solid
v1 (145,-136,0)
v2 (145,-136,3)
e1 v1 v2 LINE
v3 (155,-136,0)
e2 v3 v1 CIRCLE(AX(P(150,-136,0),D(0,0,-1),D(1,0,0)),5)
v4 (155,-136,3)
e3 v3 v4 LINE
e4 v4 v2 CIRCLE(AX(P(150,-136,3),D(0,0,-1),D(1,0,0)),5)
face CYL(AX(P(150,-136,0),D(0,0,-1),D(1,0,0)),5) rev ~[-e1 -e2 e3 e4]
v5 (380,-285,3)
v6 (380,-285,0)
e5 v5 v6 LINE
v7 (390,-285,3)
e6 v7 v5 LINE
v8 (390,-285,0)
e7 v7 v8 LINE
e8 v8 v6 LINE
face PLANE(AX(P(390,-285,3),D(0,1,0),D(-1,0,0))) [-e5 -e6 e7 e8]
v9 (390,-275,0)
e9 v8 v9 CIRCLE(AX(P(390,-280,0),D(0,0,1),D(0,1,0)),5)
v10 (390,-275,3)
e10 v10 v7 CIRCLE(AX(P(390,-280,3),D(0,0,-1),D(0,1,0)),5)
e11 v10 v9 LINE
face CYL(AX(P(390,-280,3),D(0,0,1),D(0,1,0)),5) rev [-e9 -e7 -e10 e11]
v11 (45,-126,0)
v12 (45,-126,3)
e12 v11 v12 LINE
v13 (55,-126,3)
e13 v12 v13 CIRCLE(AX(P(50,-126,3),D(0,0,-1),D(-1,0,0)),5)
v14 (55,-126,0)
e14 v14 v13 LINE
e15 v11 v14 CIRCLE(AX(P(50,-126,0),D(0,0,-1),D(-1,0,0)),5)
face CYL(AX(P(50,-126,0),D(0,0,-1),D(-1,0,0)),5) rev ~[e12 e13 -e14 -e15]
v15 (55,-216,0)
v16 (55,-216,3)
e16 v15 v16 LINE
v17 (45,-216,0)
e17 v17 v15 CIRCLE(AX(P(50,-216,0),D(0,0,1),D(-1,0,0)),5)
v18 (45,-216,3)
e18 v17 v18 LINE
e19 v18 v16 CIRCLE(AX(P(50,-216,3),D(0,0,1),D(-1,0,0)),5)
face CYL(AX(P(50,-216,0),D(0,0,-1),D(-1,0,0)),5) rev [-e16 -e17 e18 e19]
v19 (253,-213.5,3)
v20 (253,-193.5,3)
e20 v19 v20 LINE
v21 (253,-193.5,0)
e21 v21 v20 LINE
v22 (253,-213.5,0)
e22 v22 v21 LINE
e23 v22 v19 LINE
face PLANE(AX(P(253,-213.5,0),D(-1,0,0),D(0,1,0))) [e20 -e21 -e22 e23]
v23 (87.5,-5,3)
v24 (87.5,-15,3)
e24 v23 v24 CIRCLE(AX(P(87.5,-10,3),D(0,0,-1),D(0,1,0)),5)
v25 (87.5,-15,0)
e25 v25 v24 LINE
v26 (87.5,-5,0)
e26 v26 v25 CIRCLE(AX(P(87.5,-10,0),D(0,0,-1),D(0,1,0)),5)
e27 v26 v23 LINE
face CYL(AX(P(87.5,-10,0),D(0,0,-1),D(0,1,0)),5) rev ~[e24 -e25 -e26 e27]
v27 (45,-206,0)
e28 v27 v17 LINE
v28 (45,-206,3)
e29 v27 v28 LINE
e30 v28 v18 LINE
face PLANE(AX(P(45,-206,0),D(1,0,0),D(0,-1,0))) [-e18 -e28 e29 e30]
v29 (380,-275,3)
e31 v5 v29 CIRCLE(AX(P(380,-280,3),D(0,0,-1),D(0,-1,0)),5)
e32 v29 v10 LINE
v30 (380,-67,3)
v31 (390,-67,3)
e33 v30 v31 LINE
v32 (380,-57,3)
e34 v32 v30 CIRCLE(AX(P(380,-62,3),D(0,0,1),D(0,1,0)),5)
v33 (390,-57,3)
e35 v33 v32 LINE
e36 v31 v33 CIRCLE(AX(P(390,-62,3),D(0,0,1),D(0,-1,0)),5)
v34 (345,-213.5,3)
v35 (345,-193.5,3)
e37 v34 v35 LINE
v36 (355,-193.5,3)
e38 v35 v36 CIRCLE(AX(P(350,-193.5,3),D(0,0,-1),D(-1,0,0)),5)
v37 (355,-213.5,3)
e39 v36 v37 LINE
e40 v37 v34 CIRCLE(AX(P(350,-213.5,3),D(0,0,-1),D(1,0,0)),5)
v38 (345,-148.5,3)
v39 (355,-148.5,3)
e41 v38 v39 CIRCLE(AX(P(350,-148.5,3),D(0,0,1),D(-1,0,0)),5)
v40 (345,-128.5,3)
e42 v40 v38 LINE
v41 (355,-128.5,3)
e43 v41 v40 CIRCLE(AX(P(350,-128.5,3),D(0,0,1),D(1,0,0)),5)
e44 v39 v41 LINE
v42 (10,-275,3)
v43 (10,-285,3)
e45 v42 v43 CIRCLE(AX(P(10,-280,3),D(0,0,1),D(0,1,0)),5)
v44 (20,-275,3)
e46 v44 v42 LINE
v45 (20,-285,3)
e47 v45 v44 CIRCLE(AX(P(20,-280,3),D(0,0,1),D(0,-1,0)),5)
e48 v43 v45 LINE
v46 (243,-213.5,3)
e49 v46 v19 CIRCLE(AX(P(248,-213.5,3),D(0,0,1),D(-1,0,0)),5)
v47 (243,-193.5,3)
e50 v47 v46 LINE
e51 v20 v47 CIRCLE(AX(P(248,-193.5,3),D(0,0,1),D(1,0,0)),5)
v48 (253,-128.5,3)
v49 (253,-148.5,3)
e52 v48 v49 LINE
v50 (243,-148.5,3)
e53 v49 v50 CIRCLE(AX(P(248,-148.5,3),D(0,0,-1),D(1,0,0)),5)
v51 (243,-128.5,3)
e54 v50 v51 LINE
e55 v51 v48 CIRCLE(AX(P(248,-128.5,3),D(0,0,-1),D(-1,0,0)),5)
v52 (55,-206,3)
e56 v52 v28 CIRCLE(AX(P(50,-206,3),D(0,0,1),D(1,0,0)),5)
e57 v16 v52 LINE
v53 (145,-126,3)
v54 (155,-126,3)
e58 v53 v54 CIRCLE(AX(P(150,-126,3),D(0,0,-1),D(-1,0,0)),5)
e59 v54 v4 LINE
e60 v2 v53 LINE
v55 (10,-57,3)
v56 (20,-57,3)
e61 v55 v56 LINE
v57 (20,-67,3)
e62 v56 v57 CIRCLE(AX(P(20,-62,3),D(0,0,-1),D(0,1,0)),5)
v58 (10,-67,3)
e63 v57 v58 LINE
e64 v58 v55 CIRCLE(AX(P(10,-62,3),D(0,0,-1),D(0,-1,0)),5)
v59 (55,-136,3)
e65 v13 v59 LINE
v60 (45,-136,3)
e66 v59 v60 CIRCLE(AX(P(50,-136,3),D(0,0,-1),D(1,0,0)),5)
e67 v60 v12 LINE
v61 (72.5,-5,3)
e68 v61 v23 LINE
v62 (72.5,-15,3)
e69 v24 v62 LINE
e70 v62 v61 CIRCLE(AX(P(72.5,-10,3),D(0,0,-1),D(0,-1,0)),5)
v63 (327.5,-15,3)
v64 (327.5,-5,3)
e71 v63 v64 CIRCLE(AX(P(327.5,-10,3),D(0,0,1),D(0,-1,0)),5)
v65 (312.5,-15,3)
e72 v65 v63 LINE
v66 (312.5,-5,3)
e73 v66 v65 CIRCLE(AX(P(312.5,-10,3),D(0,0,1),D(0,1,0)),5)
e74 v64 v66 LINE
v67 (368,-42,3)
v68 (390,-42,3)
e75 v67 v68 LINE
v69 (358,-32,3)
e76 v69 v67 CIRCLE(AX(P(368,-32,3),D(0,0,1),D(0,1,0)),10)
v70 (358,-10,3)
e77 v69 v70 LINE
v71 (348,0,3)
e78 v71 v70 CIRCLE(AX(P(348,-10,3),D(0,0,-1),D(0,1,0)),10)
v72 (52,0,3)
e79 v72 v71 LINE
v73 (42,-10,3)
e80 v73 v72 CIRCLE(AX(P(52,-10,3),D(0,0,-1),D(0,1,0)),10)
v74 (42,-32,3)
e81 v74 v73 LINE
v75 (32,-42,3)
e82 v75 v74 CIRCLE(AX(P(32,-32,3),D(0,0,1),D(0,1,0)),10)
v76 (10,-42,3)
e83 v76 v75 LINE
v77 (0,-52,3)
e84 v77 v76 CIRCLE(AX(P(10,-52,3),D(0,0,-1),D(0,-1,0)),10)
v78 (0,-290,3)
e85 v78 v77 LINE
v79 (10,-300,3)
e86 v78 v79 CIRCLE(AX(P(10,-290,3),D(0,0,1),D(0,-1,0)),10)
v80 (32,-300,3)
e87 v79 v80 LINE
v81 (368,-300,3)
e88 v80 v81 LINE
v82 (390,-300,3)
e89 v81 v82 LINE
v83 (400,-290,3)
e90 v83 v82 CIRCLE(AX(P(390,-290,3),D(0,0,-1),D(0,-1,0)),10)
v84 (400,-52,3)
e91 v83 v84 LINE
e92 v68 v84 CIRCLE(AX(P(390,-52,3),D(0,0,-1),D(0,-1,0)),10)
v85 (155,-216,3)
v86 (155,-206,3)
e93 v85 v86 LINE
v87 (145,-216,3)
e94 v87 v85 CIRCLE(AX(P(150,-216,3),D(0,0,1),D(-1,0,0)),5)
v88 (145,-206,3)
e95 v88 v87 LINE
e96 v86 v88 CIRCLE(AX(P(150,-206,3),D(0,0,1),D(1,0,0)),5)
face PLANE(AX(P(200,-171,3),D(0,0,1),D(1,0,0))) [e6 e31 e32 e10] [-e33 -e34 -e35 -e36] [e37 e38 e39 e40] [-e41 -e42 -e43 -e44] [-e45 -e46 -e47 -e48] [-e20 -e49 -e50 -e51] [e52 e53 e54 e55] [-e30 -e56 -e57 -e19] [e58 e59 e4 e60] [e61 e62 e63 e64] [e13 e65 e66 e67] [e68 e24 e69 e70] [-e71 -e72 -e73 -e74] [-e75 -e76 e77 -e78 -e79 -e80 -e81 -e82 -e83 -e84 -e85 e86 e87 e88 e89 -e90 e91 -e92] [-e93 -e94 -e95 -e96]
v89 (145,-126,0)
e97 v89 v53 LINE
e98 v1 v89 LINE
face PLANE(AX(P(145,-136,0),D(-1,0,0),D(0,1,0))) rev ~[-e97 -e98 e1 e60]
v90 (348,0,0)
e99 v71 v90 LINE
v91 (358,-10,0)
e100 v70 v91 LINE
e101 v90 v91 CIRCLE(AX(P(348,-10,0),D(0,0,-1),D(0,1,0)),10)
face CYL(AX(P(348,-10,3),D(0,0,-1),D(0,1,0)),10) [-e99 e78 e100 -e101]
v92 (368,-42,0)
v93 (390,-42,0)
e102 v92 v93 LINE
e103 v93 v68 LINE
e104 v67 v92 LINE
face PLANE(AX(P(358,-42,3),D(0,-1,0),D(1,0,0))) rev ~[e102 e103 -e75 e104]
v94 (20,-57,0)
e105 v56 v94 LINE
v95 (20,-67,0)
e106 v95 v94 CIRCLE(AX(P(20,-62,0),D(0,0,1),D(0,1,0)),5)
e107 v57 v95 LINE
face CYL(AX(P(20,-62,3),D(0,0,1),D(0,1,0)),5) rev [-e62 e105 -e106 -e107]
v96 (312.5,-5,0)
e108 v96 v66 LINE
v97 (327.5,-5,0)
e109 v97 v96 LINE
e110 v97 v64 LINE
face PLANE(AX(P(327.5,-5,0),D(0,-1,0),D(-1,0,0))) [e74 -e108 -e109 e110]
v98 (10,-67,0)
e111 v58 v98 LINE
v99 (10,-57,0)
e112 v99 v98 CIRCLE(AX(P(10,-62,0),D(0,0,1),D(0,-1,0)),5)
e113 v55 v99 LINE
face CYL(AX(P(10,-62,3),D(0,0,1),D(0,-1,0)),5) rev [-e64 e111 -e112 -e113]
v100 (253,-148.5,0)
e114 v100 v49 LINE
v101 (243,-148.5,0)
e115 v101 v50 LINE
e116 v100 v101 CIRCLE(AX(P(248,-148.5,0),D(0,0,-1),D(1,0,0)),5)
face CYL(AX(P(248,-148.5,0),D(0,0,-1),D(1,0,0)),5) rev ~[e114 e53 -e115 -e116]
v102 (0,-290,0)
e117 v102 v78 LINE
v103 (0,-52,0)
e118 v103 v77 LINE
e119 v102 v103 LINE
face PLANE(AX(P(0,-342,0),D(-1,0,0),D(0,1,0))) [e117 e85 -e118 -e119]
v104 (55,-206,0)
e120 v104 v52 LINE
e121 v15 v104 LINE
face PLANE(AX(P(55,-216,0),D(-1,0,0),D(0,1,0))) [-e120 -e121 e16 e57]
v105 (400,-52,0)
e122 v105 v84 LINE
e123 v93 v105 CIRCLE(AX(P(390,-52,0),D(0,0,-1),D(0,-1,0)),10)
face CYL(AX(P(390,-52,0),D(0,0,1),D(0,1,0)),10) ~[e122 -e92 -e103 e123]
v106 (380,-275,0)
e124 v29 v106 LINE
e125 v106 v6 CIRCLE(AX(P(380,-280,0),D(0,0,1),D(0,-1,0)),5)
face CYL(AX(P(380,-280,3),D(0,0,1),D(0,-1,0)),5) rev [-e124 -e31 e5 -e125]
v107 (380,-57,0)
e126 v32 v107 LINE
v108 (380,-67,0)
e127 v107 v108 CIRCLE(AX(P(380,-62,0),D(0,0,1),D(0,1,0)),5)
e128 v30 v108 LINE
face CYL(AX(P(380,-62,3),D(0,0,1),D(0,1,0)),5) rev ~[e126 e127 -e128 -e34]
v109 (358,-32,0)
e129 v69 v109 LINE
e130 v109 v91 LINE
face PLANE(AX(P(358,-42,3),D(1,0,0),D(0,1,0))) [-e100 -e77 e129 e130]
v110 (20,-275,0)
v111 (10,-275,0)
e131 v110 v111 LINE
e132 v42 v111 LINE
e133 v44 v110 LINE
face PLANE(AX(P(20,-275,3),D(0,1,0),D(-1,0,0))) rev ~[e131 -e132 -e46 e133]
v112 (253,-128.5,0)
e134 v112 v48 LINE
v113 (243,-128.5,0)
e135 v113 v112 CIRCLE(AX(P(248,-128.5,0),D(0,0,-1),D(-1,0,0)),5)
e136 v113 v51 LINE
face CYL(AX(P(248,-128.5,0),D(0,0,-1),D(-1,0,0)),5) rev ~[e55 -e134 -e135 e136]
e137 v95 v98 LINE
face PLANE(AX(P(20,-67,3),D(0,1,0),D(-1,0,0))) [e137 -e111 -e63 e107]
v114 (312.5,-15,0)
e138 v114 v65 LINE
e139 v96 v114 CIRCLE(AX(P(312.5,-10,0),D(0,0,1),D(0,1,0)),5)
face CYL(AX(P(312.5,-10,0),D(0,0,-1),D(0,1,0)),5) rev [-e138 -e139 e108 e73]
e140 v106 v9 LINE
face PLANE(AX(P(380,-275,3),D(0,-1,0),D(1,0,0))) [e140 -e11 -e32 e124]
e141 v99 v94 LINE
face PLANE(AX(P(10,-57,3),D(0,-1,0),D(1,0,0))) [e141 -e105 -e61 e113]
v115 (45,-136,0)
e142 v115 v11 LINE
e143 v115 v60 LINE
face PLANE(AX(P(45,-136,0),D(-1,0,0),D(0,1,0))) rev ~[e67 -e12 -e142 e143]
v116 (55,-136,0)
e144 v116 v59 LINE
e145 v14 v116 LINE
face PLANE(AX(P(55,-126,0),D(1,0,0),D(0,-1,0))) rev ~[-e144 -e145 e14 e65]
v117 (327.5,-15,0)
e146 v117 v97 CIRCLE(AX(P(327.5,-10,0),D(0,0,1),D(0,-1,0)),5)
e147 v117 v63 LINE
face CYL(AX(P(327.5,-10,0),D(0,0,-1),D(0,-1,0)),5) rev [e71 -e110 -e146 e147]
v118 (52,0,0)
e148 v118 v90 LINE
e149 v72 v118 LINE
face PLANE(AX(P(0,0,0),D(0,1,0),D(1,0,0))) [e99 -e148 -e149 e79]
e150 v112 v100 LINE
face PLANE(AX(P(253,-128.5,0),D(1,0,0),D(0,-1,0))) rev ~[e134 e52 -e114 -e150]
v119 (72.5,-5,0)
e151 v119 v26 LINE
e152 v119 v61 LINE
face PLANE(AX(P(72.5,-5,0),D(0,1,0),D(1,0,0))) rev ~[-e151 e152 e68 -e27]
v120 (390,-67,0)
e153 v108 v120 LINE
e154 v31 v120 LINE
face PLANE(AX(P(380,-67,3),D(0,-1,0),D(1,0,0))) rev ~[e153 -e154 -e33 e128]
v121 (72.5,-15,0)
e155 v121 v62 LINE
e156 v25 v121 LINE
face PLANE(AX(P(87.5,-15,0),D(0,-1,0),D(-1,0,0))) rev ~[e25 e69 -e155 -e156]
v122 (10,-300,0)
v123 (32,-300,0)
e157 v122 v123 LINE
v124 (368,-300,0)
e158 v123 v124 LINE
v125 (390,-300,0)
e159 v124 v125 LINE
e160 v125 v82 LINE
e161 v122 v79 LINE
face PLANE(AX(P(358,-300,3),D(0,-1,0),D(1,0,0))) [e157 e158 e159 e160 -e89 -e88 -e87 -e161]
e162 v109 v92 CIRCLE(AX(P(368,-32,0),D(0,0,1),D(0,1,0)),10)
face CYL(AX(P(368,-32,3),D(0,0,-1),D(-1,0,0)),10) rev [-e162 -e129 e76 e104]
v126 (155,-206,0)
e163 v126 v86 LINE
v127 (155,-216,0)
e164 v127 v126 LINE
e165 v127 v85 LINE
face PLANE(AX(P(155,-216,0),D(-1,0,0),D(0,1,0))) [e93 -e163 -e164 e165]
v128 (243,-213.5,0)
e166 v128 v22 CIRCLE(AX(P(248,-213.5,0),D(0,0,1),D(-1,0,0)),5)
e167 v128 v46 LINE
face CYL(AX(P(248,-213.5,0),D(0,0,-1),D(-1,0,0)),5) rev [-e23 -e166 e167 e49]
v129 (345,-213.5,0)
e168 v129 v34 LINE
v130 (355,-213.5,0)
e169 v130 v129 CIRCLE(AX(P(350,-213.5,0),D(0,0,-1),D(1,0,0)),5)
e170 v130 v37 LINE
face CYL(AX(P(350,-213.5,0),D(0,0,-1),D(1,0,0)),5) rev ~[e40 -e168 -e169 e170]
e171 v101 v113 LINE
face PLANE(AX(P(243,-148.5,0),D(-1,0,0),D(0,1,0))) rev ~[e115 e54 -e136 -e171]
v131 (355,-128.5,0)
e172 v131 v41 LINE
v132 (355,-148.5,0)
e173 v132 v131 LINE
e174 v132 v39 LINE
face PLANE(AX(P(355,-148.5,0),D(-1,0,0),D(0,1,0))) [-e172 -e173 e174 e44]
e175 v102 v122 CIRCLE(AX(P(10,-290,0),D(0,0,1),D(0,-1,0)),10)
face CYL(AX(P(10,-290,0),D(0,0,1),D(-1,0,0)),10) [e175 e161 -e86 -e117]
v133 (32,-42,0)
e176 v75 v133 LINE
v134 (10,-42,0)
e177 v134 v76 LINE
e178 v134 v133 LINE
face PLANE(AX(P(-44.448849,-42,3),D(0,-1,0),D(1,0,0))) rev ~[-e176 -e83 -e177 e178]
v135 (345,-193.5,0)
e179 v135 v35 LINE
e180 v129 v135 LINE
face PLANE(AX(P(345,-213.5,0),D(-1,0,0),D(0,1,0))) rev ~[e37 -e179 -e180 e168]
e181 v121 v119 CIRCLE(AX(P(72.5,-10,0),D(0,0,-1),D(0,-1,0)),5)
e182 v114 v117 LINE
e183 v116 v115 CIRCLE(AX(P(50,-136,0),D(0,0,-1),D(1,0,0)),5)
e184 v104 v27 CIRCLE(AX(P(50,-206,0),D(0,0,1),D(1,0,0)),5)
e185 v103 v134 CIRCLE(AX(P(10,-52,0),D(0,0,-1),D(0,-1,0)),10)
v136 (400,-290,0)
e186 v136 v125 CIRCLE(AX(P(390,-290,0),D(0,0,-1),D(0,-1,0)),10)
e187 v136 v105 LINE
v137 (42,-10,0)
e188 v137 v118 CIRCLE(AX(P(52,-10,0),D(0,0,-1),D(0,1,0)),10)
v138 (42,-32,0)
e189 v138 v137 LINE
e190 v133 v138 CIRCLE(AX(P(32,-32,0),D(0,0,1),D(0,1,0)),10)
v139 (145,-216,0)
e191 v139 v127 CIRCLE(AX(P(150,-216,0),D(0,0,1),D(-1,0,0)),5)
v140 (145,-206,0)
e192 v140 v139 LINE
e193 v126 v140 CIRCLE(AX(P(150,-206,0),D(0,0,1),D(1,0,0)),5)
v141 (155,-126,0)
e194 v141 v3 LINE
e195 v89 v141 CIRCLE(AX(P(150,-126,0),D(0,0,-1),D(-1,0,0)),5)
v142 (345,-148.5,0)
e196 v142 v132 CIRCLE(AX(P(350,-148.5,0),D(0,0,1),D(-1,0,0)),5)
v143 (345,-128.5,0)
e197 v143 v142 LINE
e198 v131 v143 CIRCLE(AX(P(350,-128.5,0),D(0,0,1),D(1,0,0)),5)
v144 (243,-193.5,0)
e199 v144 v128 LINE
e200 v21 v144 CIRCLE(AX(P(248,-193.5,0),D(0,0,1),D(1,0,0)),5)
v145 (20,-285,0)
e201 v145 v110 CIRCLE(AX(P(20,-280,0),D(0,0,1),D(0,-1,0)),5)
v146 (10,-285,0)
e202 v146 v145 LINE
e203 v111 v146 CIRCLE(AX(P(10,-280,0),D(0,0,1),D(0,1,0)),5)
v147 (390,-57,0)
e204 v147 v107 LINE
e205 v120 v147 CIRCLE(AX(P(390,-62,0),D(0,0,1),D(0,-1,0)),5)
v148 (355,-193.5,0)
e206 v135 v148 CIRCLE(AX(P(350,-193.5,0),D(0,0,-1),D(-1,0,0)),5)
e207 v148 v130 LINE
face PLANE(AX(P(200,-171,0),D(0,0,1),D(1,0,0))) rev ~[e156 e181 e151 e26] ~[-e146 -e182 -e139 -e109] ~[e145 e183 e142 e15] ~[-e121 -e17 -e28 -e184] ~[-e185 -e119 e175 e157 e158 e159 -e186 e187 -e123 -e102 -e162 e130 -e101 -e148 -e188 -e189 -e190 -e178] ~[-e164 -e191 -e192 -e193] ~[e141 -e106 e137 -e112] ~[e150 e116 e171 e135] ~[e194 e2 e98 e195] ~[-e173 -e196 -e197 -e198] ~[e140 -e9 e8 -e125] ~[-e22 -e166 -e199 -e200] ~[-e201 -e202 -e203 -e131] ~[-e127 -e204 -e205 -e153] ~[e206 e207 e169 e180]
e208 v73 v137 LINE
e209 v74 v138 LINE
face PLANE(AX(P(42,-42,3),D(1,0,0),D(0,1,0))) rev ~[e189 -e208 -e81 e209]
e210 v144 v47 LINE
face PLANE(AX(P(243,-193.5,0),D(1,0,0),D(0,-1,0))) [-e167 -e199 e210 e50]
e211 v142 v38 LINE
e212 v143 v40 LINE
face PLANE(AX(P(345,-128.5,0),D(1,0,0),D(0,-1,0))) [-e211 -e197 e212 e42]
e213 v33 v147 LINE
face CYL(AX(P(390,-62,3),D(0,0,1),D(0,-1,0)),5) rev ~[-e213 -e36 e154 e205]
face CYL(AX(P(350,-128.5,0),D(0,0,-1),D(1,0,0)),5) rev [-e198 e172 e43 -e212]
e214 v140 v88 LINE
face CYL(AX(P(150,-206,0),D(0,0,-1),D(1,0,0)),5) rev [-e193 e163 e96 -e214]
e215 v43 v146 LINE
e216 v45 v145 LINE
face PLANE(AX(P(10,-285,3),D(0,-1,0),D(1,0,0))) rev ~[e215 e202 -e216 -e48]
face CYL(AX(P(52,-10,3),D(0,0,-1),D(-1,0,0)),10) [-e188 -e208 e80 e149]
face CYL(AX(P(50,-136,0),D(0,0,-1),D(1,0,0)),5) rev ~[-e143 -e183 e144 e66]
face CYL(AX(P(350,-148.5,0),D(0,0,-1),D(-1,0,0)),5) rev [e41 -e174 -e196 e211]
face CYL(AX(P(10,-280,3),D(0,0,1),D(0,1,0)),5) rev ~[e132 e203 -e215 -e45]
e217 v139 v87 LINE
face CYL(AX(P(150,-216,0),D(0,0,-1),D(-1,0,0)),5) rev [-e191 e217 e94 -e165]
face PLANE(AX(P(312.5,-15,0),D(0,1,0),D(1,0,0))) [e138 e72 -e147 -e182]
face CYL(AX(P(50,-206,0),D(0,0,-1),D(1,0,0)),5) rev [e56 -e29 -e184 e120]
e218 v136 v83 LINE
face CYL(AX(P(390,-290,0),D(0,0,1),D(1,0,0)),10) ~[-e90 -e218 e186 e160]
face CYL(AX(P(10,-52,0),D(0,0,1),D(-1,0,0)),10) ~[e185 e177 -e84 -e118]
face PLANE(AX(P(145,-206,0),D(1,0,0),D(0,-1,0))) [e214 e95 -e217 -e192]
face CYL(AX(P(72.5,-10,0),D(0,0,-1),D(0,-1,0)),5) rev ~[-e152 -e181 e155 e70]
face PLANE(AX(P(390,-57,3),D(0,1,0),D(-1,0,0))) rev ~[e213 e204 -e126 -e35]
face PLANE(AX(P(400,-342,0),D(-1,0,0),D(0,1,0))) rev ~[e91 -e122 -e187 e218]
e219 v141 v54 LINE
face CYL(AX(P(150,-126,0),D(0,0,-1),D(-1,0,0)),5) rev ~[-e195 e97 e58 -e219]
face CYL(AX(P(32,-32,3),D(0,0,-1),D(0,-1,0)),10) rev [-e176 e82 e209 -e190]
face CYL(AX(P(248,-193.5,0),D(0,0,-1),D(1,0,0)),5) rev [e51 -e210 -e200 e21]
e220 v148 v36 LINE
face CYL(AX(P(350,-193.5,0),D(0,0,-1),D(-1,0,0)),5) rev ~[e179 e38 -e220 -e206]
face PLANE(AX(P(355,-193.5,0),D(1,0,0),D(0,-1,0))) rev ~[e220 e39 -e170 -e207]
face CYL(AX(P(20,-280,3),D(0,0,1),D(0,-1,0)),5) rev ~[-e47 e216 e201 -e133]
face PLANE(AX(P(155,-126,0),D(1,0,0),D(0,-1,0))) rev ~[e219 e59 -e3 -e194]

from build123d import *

# Parameters (mm, degrees)
SKETCH1_W           = 400
SKETCH1_H           = 342
BOSS_EXTRUDE1_DEPTH = 3
SKETCH3_W           = 86.448848967
SKETCH3_H           = 526.142419803
CUT_EXTRUDE2_DEPTH  = 527.282243668
FILLET1_R           = 10
CUT_EXTRUDE3_DEPTH  = 527.282243668
SKETCH5_W           = 336
SKETCH5_H           = 215.570811559
CUT_EXTRUDE4_DEPTH  = 10


with BuildPart() as part:
    # Sketch1 → Boss-Extrude1 (new body)
    with BuildSketch(Plane.XY):
        with Locations((200, -171)):
            Rectangle(SKETCH1_W, SKETCH1_H)
        with BuildLine():
            Line((253, -128.5), (253, -148.5))
            ThreePointArc((253, -148.5), (248, -153.5), (243, -148.5))
            Line((243, -148.5), (243, -128.5))
            ThreePointArc((243, -128.5), (248, -123.5), (253, -128.5))
        make_face(mode=Mode.SUBTRACT)
        with BuildLine():
            Line((345, -128.5), (345, -148.5))
            ThreePointArc((345, -148.5), (350, -153.5), (355, -148.5))
            Line((355, -148.5), (355, -128.5))
            ThreePointArc((355, -128.5), (350, -123.5), (345, -128.5))
        make_face(mode=Mode.SUBTRACT)
        with BuildLine():
            Line((345, -213.5), (345, -193.5))
            ThreePointArc((345, -193.5), (350, -188.5), (355, -193.5))
            Line((355, -193.5), (355, -213.5))
            ThreePointArc((355, -213.5), (350, -218.5), (345, -213.5))
        make_face(mode=Mode.SUBTRACT)
        with BuildLine():
            Line((253, -213.5), (253, -193.5))
            ThreePointArc((253, -193.5), (248, -188.5), (243, -193.5))
            Line((243, -193.5), (243, -213.5))
            ThreePointArc((243, -213.5), (248, -218.5), (253, -213.5))
        make_face(mode=Mode.SUBTRACT)
        with BuildLine():
            Line((72.5, -5), (87.5, -5))
            ThreePointArc((87.5, -5), (92.5, -10), (87.5, -15))
            Line((87.5, -15), (72.5, -15))
            ThreePointArc((72.5, -15), (67.5, -10), (72.5, -5))
        make_face(mode=Mode.SUBTRACT)
        with BuildLine():
            Line((327.5, -5), (312.5, -5))
            ThreePointArc((312.5, -5), (307.5, -10), (312.5, -15))
            Line((312.5, -15), (327.5, -15))
            ThreePointArc((327.5, -15), (332.5, -10), (327.5, -5))
        make_face(mode=Mode.SUBTRACT)
        with BuildLine():
            Line((327.5, -337), (312.5, -337))
            ThreePointArc((312.5, -337), (307.5, -332), (312.5, -327))
            Line((312.5, -327), (327.5, -327))
            ThreePointArc((327.5, -327), (332.5, -332), (327.5, -337))
        make_face(mode=Mode.SUBTRACT)
        with BuildLine():
            Line((72.5, -337), (87.5, -337))
            ThreePointArc((87.5, -337), (92.5, -332), (87.5, -327))
            Line((87.5, -327), (72.5, -327))
            ThreePointArc((72.5, -327), (67.5, -332), (72.5, -337))
        make_face(mode=Mode.SUBTRACT)
        with BuildLine():
            Line((55, -126), (55, -136))
            ThreePointArc((55, -136), (50, -141), (45, -136))
            Line((45, -136), (45, -126))
            ThreePointArc((45, -126), (50, -121), (55, -126))
        make_face(mode=Mode.SUBTRACT)
        with BuildLine():
            Line((155, -126), (155, -136))
            ThreePointArc((155, -136), (150, -141), (145, -136))
            Line((145, -136), (145, -126))
            ThreePointArc((145, -126), (150, -121), (155, -126))
        make_face(mode=Mode.SUBTRACT)
        with BuildLine():
            Line((155, -216), (155, -206))
            ThreePointArc((155, -206), (150, -201), (145, -206))
            Line((145, -206), (145, -216))
            ThreePointArc((145, -216), (150, -221), (155, -216))
        make_face(mode=Mode.SUBTRACT)
        with BuildLine():
            Line((55, -216), (55, -206))
            ThreePointArc((55, -206), (50, -201), (45, -206))
            Line((45, -206), (45, -216))
            ThreePointArc((45, -216), (50, -221), (55, -216))
        make_face(mode=Mode.SUBTRACT)
    extrude(amount=BOSS_EXTRUDE1_DEPTH)

    # Sketch3 → Cut-Extrude2 (cut, through all)
    with BuildSketch(Plane.XY.offset(3)):
        with Locations((-1.224424484, -563.071209901)):
            Rectangle(SKETCH3_W, SKETCH3_H)
        with Locations((401.224424484, -563.071209901)):
            Rectangle(SKETCH3_W, SKETCH3_H)
        with Locations((401.224424484, 221.071209902)):
            Rectangle(SKETCH3_W, SKETCH3_H)
        with Locations((-1.224424484, 221.071209902)):
            Rectangle(SKETCH3_W, SKETCH3_H)
    extrude(amount=-CUT_EXTRUDE2_DEPTH, mode=Mode.SUBTRACT)

    # Fillet1
    fillet1_edges = [part.edges().sort_by_distance(p)[0] for p in [
        (358, 0, 1.5),
        (42, 0, 1.5),
        (400, -300, 1.5),
        (400, -42, 1.5),
        (42, -342, 1.5),
        (358, -342, 1.5),
        (0, -300, 1.5),
        (0, -42, 1.5),
        (42, -42, 1.5),
        (358, -42, 1.5),
        (358, -300, 1.5),
        (42, -300, 1.5),
    ]]
    fillet(fillet1_edges, radius=FILLET1_R)

    # Sketch4 → Cut-Extrude3 (cut, through all)
    with BuildSketch(Plane.XY.offset(3)):
        with BuildLine():
            Line((10, -57), (20, -57))
            ThreePointArc((20, -57), (25, -62), (20, -67))
            Line((20, -67), (10, -67))
            ThreePointArc((10, -67), (5, -62), (10, -57))
        make_face()
        with BuildLine():
            Line((390, -57), (380, -57))
            ThreePointArc((380, -57), (375, -62), (380, -67))
            Line((380, -67), (390, -67))
            ThreePointArc((390, -67), (395, -62), (390, -57))
        make_face()
        with BuildLine():
            Line((390, -285), (380, -285))
            ThreePointArc((380, -285), (375, -280), (380, -275))
            Line((380, -275), (390, -275))
            ThreePointArc((390, -275), (395, -280), (390, -285))
        make_face()
        with BuildLine():
            Line((10, -285), (20, -285))
            ThreePointArc((20, -285), (25, -280), (20, -275))
            Line((20, -275), (10, -275))
            ThreePointArc((10, -275), (5, -280), (10, -285))
        make_face()
    extrude(amount=-CUT_EXTRUDE3_DEPTH, mode=Mode.SUBTRACT)

    # Sketch5 → Cut-Extrude4 (cut)
    with BuildSketch(Plane.XY.offset(3)):
        with Locations((200, -407.78540578)):
            Rectangle(SKETCH5_W, SKETCH5_H)
    extrude(amount=-CUT_EXTRUDE4_DEPTH, mode=Mode.SUBTRACT)


solid = part.part
